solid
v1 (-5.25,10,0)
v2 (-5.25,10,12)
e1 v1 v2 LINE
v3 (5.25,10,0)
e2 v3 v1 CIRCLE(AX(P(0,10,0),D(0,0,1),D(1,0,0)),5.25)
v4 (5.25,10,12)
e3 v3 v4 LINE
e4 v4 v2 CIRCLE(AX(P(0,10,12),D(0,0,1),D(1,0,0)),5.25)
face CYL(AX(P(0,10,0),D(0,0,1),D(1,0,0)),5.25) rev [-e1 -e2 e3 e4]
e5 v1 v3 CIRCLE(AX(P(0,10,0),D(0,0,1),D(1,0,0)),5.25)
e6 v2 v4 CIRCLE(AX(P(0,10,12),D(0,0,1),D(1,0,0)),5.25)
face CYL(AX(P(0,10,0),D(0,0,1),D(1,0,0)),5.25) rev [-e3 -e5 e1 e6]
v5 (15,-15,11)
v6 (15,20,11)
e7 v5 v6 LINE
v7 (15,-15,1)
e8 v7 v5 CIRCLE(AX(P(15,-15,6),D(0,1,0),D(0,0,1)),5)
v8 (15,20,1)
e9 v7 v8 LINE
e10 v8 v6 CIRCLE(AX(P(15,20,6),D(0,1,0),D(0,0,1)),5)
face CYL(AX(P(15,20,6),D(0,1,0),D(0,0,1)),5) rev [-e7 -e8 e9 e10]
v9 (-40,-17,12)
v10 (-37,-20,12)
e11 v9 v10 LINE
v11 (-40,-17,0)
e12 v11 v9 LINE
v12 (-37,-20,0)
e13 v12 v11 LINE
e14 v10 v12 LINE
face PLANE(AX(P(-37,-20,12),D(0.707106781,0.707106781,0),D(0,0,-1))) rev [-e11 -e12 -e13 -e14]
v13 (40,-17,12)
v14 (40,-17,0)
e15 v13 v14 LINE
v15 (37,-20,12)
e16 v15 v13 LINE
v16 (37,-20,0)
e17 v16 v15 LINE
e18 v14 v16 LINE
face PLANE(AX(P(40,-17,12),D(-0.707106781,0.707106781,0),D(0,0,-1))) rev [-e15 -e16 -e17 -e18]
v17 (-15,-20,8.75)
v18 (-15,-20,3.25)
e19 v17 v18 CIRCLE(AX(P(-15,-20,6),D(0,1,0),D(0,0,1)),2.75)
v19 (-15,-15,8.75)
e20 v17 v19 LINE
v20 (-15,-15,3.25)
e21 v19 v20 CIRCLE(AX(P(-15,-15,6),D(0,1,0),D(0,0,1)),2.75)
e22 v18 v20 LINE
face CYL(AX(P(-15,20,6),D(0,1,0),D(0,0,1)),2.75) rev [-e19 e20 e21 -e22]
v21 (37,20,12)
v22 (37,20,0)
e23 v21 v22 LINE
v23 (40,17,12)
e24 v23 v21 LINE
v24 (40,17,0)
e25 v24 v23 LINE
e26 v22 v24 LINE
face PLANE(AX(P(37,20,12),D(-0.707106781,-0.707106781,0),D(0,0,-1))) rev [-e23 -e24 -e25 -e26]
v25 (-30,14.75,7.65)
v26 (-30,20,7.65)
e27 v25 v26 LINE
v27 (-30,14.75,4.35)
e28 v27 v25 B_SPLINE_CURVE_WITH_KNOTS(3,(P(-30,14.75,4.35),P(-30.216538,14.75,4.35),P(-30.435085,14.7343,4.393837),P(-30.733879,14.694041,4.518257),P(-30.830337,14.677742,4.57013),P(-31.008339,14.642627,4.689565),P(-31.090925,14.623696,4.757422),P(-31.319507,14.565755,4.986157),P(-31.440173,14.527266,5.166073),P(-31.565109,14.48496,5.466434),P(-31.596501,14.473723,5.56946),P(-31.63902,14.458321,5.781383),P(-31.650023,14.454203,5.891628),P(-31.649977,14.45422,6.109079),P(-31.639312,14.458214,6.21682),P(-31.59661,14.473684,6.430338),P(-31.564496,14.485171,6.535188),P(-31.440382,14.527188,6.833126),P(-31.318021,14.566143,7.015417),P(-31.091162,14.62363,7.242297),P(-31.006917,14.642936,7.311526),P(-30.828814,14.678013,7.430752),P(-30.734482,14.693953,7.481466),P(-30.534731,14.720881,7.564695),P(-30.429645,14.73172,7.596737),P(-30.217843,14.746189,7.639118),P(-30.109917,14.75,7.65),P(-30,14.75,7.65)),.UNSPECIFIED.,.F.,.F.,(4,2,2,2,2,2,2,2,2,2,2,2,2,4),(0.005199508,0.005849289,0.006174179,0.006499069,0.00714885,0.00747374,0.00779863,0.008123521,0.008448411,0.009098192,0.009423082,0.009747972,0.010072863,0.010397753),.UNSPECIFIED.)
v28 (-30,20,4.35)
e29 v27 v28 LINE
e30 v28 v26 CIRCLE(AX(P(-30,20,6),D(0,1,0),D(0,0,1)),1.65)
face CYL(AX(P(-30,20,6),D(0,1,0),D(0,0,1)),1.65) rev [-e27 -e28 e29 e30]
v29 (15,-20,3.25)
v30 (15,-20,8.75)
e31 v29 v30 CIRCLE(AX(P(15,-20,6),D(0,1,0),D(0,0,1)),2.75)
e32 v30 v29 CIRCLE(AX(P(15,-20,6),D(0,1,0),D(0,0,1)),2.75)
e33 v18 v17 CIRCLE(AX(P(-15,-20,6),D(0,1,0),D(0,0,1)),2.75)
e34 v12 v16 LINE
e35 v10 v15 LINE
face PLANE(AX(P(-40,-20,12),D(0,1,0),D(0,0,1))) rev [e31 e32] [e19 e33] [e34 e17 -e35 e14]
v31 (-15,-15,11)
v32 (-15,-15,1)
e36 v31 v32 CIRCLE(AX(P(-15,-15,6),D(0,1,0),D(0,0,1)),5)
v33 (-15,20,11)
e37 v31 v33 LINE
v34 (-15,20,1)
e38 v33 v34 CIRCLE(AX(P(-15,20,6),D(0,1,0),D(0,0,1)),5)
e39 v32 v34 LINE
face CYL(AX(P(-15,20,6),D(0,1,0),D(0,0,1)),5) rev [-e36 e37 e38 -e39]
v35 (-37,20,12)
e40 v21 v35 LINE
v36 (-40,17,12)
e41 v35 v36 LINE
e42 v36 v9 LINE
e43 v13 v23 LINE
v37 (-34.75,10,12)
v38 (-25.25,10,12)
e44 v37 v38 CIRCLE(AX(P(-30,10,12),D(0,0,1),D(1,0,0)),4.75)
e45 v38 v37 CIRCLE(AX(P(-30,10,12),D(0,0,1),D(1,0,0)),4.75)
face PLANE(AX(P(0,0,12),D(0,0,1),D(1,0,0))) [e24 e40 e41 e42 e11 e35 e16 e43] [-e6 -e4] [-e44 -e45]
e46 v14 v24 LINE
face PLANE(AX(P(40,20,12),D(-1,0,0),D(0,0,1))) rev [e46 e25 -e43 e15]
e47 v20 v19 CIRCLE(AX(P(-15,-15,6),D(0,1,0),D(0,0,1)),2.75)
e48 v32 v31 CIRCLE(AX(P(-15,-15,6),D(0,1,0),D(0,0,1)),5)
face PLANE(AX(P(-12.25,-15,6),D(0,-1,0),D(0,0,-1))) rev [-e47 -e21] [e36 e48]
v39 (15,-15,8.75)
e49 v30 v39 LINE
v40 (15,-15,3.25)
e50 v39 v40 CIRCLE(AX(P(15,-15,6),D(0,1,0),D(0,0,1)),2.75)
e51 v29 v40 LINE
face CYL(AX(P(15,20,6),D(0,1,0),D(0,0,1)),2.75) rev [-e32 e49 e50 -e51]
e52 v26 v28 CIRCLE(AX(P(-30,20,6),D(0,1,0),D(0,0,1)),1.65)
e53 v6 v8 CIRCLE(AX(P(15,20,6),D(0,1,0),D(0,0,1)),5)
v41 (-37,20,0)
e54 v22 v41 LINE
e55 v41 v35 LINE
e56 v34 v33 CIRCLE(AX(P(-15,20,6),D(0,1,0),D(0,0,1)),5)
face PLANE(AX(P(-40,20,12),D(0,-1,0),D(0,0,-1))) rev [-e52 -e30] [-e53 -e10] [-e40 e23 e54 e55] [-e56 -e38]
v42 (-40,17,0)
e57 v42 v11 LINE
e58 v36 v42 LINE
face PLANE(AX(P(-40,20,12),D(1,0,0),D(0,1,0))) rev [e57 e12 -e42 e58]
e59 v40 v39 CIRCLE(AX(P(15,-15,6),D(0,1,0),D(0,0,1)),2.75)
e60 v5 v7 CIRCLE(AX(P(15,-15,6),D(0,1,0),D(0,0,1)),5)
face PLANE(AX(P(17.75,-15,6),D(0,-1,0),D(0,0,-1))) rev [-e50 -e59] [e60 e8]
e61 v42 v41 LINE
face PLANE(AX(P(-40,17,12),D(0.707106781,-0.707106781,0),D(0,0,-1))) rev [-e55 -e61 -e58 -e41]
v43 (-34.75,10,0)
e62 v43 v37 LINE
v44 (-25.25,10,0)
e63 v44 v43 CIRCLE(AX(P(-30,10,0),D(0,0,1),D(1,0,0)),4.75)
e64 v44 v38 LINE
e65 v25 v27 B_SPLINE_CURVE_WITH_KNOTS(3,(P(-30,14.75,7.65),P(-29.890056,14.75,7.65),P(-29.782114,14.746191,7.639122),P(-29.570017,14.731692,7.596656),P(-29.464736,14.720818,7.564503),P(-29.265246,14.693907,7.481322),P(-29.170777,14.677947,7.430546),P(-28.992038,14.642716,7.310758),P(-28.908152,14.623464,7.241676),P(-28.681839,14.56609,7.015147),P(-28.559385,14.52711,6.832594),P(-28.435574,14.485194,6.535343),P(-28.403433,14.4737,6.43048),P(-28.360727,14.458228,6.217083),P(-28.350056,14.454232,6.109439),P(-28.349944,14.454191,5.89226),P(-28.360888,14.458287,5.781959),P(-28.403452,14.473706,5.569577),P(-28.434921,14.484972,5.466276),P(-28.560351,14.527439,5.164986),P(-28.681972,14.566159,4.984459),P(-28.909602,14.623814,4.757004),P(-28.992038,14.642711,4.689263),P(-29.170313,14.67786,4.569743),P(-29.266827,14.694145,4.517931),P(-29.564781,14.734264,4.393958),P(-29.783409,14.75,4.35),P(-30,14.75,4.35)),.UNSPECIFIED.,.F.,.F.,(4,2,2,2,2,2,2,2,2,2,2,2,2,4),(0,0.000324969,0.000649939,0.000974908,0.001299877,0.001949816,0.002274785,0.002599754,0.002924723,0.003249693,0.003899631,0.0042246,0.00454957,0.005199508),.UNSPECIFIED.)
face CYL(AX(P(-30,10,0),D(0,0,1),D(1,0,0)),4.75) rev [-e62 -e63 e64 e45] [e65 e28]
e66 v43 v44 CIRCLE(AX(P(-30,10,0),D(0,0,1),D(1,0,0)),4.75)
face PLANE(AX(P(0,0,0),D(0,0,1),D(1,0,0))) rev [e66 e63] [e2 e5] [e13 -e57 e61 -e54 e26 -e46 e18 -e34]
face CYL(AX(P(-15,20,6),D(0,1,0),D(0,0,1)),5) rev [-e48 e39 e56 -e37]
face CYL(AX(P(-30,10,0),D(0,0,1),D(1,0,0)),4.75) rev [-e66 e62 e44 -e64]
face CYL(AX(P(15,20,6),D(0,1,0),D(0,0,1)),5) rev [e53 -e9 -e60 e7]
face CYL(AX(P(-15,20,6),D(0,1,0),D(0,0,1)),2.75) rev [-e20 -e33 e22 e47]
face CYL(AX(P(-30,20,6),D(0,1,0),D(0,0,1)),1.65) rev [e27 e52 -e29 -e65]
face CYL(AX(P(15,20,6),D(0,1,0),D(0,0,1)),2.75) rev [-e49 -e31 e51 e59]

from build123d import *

# Parameters (mm, degrees)
SKETCH1_W                                           = 80
SKETCH1_H                                           = 40
BOSS_EXTRUDE1_DEPTH                                 = 12
SKETCH2_R                                           = 5.25
SKETCH2_R_2                                         = 4.75
CUT_EXTRUDE1_DEPTH                                  = 47.303347611
CBORE_FOR_M5_HEX_SOCKET_HEAD_CAP_SCREW1_D           = 5.5
CBORE_FOR_M5_HEX_SOCKET_HEAD_CAP_SCREW1_CBORE_D     = 10
CBORE_FOR_M5_HEX_SOCKET_HEAD_CAP_SCREW1_CBORE_DEPTH = 35
CHAMFER1_SIZE                                       = 3
M4_TAPPED_HOLE1_D                                   = 3.3
M4_TAPPED_HOLE1_DEPTH                               = 10.1
M4_TAPPED_HOLE1_TIP                                 = 0.991420021


with BuildPart() as part:
    # Sketch1 → Boss-Extrude1 (new body)
    with BuildSketch(Plane.XY):
        Rectangle(SKETCH1_W, SKETCH1_H)
    extrude(amount=BOSS_EXTRUDE1_DEPTH)

    # Sketch2 → Cut-Extrude1 (cut, through all)
    with BuildSketch(Plane.XY.offset(12)):
        with Locations((0, 10)):
            Circle(SKETCH2_R)
        with Locations((-30, 10)):
            Circle(SKETCH2_R_2)
    extrude(amount=-CUT_EXTRUDE1_DEPTH, mode=Mode.SUBTRACT)

    # CBORE for M5 Hex Socket Head Cap Screw1 (through all)
    with Locations(Plane(origin=(0, 20, 0), x_dir=(1, 0, 0), z_dir=(0, 1, 0))):
        with Locations((-15, -6), (15, -6)):
            CounterBoreHole(CBORE_FOR_M5_HEX_SOCKET_HEAD_CAP_SCREW1_D / 2, CBORE_FOR_M5_HEX_SOCKET_HEAD_CAP_SCREW1_CBORE_D / 2, CBORE_FOR_M5_HEX_SOCKET_HEAD_CAP_SCREW1_CBORE_DEPTH)

    # Chamfer1
    chamfer1_edges = [part.edges().sort_by_distance(p)[0] for p in [
        (40, -20, 6),
        (-40, -20, 6),
        (-40, 20, 6),
        (40, 20, 6),
    ]]
    chamfer(chamfer1_edges, length=CHAMFER1_SIZE)

    # M4 Tapped Hole1
    with Locations(Plane(origin=(0, 20, 0), x_dir=(1, 0, 0), z_dir=(0, 1, 0))):
        with Locations((-30, -6)):
            Hole(M4_TAPPED_HOLE1_D / 2, depth=M4_TAPPED_HOLE1_DEPTH)
            with Locations((0, 0, -(M4_TAPPED_HOLE1_DEPTH + M4_TAPPED_HOLE1_TIP / 2))):  # 118° drill point
                Cone(0, M4_TAPPED_HOLE1_D / 2, M4_TAPPED_HOLE1_TIP, mode=Mode.SUBTRACT)


solid = part.part
